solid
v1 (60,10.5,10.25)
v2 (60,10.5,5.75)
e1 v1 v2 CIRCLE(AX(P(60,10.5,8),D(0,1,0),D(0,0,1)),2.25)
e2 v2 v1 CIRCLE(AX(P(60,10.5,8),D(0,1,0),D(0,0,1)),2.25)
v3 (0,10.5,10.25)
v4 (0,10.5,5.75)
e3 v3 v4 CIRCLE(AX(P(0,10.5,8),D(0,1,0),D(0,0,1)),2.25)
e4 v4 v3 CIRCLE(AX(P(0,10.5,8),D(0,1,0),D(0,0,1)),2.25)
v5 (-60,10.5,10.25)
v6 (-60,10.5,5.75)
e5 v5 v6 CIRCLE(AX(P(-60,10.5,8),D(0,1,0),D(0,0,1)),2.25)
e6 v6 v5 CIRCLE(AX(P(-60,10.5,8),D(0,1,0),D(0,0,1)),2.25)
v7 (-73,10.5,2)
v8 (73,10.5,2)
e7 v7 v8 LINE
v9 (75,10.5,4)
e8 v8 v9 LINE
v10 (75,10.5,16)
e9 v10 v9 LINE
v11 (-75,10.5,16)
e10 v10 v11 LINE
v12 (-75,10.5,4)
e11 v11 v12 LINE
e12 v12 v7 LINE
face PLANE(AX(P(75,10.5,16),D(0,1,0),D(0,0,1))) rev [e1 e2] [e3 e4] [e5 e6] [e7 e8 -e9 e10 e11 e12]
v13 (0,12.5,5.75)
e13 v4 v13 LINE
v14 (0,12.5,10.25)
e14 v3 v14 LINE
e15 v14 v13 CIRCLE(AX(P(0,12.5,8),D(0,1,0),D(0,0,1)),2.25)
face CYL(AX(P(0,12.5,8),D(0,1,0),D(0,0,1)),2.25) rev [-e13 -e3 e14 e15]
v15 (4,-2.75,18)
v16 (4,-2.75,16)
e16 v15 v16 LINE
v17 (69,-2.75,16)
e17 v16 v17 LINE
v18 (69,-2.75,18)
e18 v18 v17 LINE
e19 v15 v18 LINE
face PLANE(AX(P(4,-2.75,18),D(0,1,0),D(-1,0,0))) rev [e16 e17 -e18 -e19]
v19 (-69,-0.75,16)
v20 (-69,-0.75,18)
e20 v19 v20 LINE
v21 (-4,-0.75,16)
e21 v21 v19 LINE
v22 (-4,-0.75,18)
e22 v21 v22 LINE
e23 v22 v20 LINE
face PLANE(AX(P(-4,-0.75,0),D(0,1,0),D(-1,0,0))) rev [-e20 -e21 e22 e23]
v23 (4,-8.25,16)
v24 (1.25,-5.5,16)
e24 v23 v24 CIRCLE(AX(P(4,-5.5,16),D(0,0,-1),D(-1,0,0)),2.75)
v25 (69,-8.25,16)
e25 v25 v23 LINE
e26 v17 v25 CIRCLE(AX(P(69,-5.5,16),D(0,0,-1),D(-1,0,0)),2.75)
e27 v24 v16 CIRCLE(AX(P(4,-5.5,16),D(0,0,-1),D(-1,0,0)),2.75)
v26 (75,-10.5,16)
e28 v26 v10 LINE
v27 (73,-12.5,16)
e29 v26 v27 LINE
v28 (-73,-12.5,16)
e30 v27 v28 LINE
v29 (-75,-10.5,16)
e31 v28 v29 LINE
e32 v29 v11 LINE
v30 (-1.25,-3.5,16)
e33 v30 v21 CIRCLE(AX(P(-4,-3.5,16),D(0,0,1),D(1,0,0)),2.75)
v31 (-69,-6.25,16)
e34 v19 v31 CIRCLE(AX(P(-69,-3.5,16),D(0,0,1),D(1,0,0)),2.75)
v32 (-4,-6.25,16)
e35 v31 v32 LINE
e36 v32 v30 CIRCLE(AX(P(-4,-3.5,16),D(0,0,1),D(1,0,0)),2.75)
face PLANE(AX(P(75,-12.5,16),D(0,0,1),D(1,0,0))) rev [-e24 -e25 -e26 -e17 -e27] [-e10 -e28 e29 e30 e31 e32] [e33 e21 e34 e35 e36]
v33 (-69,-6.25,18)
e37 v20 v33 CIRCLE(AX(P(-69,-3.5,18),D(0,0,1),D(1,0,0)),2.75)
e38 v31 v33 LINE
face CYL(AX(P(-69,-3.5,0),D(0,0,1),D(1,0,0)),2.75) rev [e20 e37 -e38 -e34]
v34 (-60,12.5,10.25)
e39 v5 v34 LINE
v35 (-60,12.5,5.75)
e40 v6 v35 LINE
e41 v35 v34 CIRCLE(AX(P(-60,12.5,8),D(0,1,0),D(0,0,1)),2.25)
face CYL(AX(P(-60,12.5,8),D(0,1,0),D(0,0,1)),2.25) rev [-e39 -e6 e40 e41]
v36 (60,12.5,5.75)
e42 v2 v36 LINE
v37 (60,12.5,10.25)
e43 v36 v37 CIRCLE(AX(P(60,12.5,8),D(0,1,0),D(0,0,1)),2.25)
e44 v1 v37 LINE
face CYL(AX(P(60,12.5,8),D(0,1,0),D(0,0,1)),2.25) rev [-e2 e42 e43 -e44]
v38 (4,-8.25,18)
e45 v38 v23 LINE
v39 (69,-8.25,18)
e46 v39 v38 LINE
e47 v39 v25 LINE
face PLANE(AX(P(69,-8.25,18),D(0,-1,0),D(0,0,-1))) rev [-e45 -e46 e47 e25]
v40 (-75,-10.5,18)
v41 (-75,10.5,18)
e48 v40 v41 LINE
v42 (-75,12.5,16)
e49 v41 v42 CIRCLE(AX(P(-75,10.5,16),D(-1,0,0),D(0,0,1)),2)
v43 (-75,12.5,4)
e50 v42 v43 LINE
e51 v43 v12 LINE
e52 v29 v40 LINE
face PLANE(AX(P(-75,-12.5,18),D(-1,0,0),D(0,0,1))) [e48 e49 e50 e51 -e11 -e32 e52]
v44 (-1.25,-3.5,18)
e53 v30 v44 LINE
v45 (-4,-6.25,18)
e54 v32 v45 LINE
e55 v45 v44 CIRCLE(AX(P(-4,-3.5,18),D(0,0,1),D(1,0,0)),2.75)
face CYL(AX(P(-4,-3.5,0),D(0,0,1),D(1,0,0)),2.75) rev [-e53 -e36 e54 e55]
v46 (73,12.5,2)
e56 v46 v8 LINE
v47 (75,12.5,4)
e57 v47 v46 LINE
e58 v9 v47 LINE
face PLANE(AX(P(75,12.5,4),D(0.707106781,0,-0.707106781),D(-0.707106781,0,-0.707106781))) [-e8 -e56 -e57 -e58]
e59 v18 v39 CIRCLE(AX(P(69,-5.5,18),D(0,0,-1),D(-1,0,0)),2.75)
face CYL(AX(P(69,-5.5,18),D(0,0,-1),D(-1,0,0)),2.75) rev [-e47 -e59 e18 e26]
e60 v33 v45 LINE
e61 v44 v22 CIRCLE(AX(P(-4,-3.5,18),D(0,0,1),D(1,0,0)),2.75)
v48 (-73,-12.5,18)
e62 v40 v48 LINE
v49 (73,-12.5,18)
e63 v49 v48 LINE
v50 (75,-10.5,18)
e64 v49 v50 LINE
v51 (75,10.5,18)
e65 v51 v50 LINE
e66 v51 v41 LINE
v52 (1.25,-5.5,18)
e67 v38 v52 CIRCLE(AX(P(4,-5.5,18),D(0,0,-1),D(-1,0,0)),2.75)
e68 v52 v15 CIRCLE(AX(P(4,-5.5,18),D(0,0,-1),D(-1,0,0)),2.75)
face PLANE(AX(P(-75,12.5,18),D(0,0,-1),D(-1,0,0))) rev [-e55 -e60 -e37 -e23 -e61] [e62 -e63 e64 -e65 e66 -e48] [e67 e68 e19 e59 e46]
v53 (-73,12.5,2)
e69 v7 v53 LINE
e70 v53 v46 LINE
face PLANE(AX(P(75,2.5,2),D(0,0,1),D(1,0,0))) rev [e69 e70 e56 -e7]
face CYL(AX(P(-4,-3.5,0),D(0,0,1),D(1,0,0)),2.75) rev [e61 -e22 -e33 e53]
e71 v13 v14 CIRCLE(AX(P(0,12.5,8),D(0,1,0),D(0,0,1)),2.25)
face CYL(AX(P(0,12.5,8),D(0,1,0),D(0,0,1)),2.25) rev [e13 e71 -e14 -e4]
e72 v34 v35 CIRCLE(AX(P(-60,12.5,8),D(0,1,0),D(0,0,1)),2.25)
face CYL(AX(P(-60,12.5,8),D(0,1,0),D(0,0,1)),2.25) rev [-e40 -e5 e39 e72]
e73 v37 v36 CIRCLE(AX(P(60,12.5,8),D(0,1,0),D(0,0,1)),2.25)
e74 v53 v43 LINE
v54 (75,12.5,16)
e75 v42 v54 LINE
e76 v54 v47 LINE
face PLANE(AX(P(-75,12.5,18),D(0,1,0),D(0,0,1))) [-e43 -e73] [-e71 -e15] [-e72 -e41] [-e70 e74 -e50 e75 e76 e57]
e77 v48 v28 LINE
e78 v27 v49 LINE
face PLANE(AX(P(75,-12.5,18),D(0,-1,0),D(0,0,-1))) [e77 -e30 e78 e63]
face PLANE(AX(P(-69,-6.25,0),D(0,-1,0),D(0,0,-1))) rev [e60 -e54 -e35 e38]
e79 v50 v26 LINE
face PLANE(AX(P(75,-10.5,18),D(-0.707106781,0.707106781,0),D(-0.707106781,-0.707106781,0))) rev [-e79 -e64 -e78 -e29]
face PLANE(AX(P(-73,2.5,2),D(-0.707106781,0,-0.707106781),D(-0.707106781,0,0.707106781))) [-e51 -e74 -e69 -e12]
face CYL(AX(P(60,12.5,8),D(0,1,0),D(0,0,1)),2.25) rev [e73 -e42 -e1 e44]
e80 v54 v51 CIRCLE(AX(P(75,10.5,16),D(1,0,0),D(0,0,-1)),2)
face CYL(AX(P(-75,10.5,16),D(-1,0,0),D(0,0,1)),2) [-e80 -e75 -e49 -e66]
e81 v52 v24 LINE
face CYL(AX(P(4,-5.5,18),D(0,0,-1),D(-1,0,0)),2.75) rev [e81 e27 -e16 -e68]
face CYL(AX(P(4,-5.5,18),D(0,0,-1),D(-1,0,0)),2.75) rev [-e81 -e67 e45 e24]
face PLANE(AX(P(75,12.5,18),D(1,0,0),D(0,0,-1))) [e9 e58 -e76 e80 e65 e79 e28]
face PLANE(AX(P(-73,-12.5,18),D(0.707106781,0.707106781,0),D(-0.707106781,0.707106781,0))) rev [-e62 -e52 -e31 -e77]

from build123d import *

# Parameters (mm, degrees)
SKETCH_1_W             = 150
SKETCH_1_H             = 25
BOSS_EXTRUDE_1_DEPTH   = 18
SKETCH_2_W             = 16
SKETCH_2_H             = 23
CUT_EXTRUDE_1_DEPTH    = 152.592381075
CUT_EXTRUDE_2_DEPTH    = 78.699742599
CUT_EXTRUDE_3_DEPTH    = 79.136099212
F_4_5_4_5_HOLE_1_D     = 4.5
F_4_5_4_5_HOLE_1_DEPTH = 15
F_4_5_4_5_HOLE_1_TIP   = 1.351936393
F_4_5_4_5_HOLE_3_D     = 4.5
F_4_5_4_5_HOLE_3_DEPTH = 15
F_4_5_4_5_HOLE_3_TIP   = 1.351936393
F_4_5_4_5_HOLE_2_D     = 4.5
F_4_5_4_5_HOLE_2_DEPTH = 15
F_4_5_4_5_HOLE_2_TIP   = 1.351936393
CHAMFER_1_SIZE         = 2
CHAMFER_3_SIZE         = 2
FILLET_1_R             = 2
SKETCH_11_W            = 150
SKETCH_11_H            = 2
CUT_EXTRUDE_4_DEPTH    = 10
CHAMFER_4_SIZE         = 2


with BuildPart() as part:
    # Sketch 1 → Boss-Extrude 1 (new body)
    with BuildSketch(Plane(origin=(0, 0, 0), x_dir=(-1, 0, 0), z_dir=(0, 0, -1))):
        Rectangle(SKETCH_1_W, SKETCH_1_H)
    extrude(amount=-BOSS_EXTRUDE_1_DEPTH)

    # Sketch 2 → Cut-Extrude 1 (cut, through all)
    with BuildSketch(Plane.ZY.offset(75)):
        with Locations((8, -1)):
            Rectangle(SKETCH_2_W, SKETCH_2_H)
    extrude(amount=-CUT_EXTRUDE_1_DEPTH, mode=Mode.SUBTRACT)

    # Sketch 3 → Cut-Extrude 2 (cut, through all)
    with BuildSketch(Plane(origin=(0, 0, 16), x_dir=(-1, 0, 0), z_dir=(0, 0, -1))):
        with BuildLine():
            Line((-4, -2.75), (-69, -2.75))
            ThreePointArc((-69, -2.75), (-71.75, -5.5), (-69, -8.25))
            Line((-69, -8.25), (-4, -8.25))
            ThreePointArc((-4, -8.25), (-1.25, -5.5), (-4, -2.75))
        make_face()
    extrude(amount=-CUT_EXTRUDE_2_DEPTH, mode=Mode.SUBTRACT)

    # Sketch 4 → Cut-Extrude 3 (cut, through all)
    with BuildSketch(Plane.XY.offset(18)):
        with BuildLine():
            Line((-69, -6.25), (-4, -6.25))
            ThreePointArc((-4, -6.25), (-1.25, -3.5), (-4, -0.75))
            Line((-4, -0.75), (-69, -0.75))
            ThreePointArc((-69, -0.75), (-71.75, -3.5), (-69, -6.25))
        make_face()
    extrude(amount=-CUT_EXTRUDE_3_DEPTH, mode=Mode.SUBTRACT)

    # Ø4.5 (4.5) Hole 1
    with Locations(Plane(origin=(0, 12.5, 0), x_dir=(-1, 0, 0), z_dir=(0, 1, 0))):
        with Locations((-60, 8)):
            Hole(F_4_5_4_5_HOLE_1_D / 2, depth=F_4_5_4_5_HOLE_1_DEPTH)
            with Locations((0, 0, -(F_4_5_4_5_HOLE_1_DEPTH + F_4_5_4_5_HOLE_1_TIP / 2))):  # 118° drill point
                Cone(0, F_4_5_4_5_HOLE_1_D / 2, F_4_5_4_5_HOLE_1_TIP, mode=Mode.SUBTRACT)

    # Ø4.5 (4.5) Hole 3
    with Locations(Plane(origin=(0, 12.5, 0), x_dir=(-1, 0, 0), z_dir=(0, 1, 0))):
        with Locations((60, 8)):
            Hole(F_4_5_4_5_HOLE_3_D / 2, depth=F_4_5_4_5_HOLE_3_DEPTH)
            with Locations((0, 0, -(F_4_5_4_5_HOLE_3_DEPTH + F_4_5_4_5_HOLE_3_TIP / 2))):  # 118° drill point
                Cone(0, F_4_5_4_5_HOLE_3_D / 2, F_4_5_4_5_HOLE_3_TIP, mode=Mode.SUBTRACT)

    # Ø4.5 (4.5) Hole 2
    with Locations(Plane(origin=(0, 12.5, 0), x_dir=(-1, 0, 0), z_dir=(0, 1, 0))):
        with Locations((0, 8)):
            Hole(F_4_5_4_5_HOLE_2_D / 2, depth=F_4_5_4_5_HOLE_2_DEPTH)
            with Locations((0, 0, -(F_4_5_4_5_HOLE_2_DEPTH + F_4_5_4_5_HOLE_2_TIP / 2))):  # 118° drill point
                Cone(0, F_4_5_4_5_HOLE_2_D / 2, F_4_5_4_5_HOLE_2_TIP, mode=Mode.SUBTRACT)

    # Chamfer 1
    chamfer_1_edges = [part.edges().sort_by_distance(p)[0] for p in [
        (75, -12.5, 17),
    ]]
    chamfer(chamfer_1_edges, length=CHAMFER_1_SIZE)

    # Chamfer 3
    chamfer_3_edges = [part.edges().sort_by_distance(p)[0] for p in [
        (-75, -12.5, 17),
    ]]
    chamfer(chamfer_3_edges, length=CHAMFER_3_SIZE)

    # Fillet 1
    fillet_1_edges = [part.edges().sort_by_distance(p)[0] for p in [
        (0, 12.5, 18),
    ]]
    fillet(fillet_1_edges, radius=FILLET_1_R)

    # Sketch 11 → Cut-Extrude 4 (cut)
    with BuildSketch(Plane(origin=(0, 12.5, 0), x_dir=(1, 0, 0), z_dir=(0, 1, 0))):
        with Locations((0, -1)):
            Rectangle(SKETCH_11_W, SKETCH_11_H)
    extrude(amount=-CUT_EXTRUDE_4_DEPTH, mode=Mode.SUBTRACT)

    # Chamfer 4
    chamfer_4_edges = [part.edges().sort_by_distance(p)[0] for p in [
        (75, 11.5, 2),
        (-75, 11.5, 2),
    ]]
    chamfer(chamfer_4_edges, length=CHAMFER_4_SIZE)


solid = part.part
